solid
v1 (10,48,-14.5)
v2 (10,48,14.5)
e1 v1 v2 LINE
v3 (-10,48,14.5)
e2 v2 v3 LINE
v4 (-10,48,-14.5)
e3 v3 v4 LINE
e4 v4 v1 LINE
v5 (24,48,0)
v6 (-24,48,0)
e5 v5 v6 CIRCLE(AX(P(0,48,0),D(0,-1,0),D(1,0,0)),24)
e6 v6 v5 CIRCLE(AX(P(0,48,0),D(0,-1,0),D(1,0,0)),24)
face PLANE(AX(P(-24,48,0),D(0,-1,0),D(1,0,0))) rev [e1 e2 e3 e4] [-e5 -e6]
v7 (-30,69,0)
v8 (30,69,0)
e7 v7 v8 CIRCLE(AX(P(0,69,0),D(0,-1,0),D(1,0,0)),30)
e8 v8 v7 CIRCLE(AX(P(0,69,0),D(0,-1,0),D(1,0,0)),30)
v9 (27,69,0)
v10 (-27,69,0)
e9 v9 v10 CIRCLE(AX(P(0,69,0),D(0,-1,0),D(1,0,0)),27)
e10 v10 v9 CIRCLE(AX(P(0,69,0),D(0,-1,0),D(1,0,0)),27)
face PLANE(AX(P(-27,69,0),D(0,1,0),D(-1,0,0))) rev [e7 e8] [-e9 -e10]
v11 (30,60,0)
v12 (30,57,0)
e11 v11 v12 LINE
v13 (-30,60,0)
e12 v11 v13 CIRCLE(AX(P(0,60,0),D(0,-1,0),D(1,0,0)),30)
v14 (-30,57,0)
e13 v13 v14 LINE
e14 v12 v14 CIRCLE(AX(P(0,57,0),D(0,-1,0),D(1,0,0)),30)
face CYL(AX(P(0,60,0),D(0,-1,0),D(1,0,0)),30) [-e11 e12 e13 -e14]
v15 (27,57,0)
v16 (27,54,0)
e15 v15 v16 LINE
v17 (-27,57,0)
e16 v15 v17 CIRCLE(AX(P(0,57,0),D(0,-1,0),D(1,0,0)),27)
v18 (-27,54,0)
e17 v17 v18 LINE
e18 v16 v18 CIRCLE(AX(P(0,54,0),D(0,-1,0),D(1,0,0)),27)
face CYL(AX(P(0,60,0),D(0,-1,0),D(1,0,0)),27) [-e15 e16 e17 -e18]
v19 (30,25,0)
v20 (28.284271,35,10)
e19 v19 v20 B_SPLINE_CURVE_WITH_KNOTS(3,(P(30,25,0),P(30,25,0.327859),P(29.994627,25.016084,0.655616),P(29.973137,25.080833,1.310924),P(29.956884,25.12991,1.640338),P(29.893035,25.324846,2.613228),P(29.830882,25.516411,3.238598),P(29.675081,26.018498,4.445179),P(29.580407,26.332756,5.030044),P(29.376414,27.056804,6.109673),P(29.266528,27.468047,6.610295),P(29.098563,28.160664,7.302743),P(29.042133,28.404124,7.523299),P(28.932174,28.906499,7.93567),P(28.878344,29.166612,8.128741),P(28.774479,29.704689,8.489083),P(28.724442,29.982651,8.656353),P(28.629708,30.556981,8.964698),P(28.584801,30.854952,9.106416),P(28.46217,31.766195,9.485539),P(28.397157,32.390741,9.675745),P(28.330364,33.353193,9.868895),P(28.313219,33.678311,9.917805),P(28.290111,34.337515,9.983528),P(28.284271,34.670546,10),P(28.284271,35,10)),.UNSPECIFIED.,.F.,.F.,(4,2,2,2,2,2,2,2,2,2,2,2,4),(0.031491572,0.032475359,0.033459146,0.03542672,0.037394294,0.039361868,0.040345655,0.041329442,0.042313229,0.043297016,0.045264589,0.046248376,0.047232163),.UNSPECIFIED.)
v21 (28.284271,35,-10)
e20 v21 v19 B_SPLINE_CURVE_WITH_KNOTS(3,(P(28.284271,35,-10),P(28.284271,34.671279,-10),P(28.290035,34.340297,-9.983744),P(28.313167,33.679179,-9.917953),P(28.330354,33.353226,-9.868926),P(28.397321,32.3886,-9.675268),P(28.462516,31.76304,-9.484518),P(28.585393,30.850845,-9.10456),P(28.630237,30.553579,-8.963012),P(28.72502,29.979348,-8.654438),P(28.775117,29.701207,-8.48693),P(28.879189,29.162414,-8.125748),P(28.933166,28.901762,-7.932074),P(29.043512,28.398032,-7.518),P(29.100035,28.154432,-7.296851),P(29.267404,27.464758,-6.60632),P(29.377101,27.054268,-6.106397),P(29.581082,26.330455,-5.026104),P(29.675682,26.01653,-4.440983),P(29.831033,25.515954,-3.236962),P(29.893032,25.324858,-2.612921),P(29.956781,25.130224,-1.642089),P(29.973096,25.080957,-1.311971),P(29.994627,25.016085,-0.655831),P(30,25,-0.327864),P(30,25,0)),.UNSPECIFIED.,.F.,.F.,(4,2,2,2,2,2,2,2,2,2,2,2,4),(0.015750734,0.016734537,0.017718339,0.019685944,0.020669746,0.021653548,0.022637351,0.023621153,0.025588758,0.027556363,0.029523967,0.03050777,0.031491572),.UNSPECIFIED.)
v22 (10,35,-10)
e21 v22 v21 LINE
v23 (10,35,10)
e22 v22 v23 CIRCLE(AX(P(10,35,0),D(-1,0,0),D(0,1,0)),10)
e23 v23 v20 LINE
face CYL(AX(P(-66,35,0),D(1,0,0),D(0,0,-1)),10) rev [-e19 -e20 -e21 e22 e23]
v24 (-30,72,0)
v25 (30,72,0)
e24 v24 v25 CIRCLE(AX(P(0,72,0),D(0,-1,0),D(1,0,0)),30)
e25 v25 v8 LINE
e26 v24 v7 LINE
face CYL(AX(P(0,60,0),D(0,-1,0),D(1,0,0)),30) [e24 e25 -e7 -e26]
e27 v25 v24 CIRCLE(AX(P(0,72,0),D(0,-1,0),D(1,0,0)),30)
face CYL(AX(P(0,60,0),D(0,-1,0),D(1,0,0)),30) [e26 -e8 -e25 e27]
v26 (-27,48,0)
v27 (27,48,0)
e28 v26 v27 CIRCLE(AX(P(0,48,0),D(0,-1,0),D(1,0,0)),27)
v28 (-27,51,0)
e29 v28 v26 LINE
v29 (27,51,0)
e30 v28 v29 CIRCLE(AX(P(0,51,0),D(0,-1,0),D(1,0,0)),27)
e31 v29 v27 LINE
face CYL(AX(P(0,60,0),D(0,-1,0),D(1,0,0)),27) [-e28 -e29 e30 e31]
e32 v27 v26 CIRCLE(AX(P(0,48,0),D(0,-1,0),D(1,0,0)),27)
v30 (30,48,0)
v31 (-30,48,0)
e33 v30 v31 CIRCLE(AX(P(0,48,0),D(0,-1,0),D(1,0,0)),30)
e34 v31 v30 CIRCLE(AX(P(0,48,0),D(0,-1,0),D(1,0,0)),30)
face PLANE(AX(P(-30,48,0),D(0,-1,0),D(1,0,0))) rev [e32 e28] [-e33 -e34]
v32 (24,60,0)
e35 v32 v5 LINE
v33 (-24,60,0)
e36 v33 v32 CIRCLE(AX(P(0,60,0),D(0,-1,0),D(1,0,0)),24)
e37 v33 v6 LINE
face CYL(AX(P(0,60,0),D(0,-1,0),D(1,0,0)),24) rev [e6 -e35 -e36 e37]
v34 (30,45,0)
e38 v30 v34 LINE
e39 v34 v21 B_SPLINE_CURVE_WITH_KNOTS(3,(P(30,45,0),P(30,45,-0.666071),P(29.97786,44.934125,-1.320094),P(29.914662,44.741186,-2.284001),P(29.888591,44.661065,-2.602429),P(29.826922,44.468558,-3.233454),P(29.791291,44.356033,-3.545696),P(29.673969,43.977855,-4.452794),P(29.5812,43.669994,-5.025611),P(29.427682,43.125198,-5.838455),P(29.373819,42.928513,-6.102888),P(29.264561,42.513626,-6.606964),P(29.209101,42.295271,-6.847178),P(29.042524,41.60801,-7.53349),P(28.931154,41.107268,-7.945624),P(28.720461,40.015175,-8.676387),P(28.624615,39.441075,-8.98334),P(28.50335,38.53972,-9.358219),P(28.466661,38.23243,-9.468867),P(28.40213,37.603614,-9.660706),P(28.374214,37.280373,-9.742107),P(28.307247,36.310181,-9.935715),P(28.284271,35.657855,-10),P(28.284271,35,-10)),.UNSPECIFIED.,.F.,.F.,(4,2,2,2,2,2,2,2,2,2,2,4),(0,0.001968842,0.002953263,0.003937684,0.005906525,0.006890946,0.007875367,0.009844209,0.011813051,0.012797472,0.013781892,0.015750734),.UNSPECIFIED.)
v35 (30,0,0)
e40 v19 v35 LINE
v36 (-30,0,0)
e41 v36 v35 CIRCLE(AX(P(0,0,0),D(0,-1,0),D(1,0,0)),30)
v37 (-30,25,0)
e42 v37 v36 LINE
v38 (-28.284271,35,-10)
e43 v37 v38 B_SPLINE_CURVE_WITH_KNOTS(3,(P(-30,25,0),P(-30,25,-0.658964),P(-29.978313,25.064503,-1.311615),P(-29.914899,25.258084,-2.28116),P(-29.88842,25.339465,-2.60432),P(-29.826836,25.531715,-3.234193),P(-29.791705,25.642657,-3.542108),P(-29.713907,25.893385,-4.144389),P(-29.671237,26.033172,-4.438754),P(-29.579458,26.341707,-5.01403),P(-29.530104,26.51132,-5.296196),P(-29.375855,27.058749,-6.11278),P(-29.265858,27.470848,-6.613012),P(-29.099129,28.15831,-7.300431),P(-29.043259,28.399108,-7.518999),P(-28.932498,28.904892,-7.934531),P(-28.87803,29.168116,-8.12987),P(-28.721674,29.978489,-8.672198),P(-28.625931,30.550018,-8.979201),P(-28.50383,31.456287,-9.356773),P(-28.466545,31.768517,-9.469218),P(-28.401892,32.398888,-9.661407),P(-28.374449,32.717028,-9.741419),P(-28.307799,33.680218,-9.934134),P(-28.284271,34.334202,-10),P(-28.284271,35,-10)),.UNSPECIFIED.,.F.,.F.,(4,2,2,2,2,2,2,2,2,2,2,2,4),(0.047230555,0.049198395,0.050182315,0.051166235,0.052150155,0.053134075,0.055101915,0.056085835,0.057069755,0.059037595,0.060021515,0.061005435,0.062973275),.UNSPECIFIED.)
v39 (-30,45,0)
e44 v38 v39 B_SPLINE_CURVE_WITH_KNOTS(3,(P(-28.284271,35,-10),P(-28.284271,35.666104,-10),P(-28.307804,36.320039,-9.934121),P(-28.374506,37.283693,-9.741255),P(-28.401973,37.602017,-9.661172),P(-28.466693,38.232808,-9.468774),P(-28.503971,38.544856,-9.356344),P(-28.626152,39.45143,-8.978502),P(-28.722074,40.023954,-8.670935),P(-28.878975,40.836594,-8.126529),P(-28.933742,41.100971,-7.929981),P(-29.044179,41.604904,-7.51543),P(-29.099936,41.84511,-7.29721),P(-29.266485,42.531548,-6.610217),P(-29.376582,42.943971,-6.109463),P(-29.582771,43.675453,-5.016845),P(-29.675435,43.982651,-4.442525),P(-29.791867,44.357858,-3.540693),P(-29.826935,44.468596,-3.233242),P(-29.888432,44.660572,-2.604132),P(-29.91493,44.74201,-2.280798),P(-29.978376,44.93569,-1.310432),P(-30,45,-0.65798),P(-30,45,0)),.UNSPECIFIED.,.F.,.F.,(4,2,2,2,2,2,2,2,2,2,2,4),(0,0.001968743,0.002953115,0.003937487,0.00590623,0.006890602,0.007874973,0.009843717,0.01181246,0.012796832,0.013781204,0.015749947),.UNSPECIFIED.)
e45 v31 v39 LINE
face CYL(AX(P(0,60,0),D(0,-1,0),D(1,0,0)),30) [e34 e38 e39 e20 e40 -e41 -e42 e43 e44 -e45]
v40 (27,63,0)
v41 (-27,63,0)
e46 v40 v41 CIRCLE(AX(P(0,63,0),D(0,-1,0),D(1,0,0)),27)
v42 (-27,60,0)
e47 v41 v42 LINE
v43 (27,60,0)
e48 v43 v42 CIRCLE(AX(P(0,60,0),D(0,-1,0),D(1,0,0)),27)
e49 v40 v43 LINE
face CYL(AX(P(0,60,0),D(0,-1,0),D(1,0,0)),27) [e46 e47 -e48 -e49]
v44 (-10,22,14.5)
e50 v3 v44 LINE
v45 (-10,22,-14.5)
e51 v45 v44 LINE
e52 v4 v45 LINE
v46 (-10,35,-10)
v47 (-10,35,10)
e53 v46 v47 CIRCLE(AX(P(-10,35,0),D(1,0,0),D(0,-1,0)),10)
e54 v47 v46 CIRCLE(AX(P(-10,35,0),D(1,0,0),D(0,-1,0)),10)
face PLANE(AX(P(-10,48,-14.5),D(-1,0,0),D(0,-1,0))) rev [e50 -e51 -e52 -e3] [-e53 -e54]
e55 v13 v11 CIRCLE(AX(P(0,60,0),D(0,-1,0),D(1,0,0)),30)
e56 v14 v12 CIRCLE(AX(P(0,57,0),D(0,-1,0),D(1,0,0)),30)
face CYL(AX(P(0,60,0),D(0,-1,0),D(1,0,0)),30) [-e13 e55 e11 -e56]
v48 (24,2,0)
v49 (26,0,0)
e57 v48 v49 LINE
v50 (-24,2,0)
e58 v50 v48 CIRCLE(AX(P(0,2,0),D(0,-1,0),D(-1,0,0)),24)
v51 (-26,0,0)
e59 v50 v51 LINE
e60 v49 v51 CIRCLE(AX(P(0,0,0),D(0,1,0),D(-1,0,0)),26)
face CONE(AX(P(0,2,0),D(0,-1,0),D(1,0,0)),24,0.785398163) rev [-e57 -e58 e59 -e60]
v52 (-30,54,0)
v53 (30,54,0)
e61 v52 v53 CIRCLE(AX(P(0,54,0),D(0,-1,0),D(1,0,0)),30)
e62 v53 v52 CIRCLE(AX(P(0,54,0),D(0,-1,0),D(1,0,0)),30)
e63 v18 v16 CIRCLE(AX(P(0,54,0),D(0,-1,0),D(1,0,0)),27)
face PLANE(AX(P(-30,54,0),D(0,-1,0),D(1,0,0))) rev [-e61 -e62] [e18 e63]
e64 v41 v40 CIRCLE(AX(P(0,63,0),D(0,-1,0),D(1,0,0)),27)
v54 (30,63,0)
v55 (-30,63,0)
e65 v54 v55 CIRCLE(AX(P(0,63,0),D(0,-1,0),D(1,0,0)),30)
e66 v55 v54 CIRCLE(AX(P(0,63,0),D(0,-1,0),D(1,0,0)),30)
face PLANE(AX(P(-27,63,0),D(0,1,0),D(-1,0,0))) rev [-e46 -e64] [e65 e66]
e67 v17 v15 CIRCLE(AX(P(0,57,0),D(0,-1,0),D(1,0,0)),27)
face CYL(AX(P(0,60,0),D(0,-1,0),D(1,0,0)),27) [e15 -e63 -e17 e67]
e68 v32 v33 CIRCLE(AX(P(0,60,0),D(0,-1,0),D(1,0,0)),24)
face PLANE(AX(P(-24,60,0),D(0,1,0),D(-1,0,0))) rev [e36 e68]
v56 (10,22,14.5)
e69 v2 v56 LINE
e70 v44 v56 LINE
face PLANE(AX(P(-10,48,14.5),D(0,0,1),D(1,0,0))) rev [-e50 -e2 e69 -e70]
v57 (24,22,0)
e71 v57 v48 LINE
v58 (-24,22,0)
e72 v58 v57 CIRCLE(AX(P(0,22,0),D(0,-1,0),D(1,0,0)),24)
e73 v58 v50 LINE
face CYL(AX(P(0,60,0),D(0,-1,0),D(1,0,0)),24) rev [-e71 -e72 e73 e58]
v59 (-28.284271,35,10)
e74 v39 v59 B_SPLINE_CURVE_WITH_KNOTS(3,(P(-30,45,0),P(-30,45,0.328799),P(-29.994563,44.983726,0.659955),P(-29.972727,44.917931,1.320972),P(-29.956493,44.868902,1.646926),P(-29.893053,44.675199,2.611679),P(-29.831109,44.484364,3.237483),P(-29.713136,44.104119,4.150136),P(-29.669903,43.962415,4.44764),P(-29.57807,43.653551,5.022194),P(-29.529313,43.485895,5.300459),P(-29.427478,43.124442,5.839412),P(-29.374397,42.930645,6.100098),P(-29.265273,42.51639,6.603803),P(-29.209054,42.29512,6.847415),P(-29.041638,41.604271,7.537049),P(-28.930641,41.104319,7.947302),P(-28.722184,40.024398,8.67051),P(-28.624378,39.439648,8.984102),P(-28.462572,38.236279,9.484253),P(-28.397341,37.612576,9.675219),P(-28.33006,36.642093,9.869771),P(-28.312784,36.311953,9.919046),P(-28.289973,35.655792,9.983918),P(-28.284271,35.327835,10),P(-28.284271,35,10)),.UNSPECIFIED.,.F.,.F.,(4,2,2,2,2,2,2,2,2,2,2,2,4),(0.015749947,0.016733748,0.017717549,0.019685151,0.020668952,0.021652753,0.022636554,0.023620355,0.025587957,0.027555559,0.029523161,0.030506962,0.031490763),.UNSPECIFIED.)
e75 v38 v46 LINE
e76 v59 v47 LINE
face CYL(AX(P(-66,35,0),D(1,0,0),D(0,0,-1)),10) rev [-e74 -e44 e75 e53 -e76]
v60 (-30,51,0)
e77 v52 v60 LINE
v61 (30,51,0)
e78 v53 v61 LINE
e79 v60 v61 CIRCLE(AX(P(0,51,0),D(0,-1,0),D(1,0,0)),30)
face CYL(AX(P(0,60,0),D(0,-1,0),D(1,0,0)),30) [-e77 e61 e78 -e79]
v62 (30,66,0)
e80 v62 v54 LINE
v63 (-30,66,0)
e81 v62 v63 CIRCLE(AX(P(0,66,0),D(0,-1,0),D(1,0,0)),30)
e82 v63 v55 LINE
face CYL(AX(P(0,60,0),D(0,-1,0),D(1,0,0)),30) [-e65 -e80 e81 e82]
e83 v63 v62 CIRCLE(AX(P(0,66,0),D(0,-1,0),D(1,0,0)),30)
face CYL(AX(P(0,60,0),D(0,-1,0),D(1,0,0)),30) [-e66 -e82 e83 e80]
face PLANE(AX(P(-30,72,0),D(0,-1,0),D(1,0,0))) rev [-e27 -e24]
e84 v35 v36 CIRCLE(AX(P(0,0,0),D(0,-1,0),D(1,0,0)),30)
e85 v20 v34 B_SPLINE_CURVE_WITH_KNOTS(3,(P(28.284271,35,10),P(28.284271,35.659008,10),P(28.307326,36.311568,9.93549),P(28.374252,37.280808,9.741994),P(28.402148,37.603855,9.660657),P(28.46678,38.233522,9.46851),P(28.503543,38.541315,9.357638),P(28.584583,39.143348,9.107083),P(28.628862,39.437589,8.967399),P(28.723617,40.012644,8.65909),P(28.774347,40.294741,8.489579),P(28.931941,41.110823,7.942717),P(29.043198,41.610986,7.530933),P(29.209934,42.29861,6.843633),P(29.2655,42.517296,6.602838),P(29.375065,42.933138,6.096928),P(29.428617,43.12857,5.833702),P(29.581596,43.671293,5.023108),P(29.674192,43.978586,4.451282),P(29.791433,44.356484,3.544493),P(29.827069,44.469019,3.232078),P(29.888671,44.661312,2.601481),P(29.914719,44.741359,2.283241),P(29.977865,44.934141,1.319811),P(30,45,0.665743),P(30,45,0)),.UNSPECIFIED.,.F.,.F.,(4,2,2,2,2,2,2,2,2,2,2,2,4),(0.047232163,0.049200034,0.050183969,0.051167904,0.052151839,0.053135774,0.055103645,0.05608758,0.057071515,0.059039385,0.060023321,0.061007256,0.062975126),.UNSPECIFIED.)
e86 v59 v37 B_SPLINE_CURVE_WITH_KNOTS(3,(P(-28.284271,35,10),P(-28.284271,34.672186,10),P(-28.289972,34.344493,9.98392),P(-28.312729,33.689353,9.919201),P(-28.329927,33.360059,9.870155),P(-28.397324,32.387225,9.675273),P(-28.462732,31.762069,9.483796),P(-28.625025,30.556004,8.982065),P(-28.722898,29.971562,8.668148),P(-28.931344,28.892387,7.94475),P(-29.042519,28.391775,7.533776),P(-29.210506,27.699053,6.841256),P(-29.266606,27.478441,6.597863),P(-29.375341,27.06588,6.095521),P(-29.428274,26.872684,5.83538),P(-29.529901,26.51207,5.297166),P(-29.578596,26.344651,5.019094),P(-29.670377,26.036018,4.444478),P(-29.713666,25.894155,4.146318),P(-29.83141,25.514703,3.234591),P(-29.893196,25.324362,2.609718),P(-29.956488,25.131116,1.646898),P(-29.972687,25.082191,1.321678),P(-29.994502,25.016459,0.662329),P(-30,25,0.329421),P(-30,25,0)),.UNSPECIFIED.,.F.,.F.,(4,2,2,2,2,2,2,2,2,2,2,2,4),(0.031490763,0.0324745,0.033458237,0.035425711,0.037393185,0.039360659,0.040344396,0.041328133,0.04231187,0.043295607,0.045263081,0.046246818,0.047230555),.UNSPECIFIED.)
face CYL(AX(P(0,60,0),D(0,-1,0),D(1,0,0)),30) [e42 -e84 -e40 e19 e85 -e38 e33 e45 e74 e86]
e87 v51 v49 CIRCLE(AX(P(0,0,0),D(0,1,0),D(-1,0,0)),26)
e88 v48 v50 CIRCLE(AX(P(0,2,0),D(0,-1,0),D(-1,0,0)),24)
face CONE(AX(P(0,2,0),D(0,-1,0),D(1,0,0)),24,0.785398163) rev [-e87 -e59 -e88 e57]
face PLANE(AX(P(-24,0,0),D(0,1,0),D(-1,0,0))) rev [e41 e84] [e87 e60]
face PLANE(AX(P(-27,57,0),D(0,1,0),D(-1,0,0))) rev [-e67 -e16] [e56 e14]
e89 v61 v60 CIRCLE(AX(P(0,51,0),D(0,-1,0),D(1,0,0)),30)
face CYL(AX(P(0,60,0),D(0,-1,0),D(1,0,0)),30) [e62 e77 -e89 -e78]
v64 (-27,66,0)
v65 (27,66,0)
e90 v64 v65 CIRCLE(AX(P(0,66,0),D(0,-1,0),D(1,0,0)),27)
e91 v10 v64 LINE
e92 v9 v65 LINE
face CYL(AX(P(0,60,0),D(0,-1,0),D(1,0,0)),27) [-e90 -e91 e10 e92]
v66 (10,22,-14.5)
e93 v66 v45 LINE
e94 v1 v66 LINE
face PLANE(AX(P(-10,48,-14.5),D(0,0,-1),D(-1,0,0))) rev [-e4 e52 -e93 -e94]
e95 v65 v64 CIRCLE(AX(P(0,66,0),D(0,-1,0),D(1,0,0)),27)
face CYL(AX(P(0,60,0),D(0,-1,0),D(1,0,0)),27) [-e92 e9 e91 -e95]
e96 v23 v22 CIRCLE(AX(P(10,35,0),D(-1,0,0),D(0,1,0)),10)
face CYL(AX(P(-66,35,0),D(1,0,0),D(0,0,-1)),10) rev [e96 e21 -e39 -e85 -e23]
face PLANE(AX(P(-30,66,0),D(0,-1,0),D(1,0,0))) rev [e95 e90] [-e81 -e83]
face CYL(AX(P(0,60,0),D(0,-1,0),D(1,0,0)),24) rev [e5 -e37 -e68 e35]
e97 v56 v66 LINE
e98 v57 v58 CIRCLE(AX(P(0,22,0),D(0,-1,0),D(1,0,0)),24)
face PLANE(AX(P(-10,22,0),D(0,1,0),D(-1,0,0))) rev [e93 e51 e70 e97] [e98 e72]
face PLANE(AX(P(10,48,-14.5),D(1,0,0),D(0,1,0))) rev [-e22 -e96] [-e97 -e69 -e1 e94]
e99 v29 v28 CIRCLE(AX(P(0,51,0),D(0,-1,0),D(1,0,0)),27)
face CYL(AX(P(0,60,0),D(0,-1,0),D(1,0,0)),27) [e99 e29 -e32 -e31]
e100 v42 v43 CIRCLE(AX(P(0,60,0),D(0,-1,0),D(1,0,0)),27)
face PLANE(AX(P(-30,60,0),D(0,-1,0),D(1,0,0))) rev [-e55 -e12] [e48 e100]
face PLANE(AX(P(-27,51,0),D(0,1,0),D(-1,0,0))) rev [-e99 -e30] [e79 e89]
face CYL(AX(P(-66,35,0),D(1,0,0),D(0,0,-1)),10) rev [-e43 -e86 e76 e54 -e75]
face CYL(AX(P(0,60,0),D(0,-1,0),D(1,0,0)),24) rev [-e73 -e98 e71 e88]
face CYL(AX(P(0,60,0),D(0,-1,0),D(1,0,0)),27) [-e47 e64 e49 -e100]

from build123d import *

# Parameters (mm, degrees)
PIN_BORE_SKETCH_R         = 10
GUDGEON_PIN_BORE_20_DEPTH = 66
EDGE_CHAMFER_2X45_SIZE    = 2
INNER_CAVITY_SKETCH_W     = 20
INNER_CAVITY_SKETCH_H     = 29
INNER_CAVITY_CUT_DEPTH    = 48


with BuildPart() as part:
    # Piston Profile Sketch → Piston Body Revolve (revolve)
    with BuildSketch(Plane.XY, mode=Mode.PRIVATE) as piston_body_revolve_sk:
        Polygon((-24, 0), (-30, 0), (-30, 48), (-27, 48), (-27, 51), (-30, 51), (-30, 54), (-27, 54), (-27, 57), (-30, 57), (-30, 60), (-27, 60), (-27, 63), (-30, 63), (-30, 66), (-27, 66), (-27, 69), (-30, 69), (-30, 72), (0, 72), (0, 60), (-24, 60), (-24, 48), (-10, 48), (-10, 22), (-24, 22), align=None)
    revolve(piston_body_revolve_sk.sketch.rotate(Axis((0, 60, 0), (0, 1, 0)), 180), axis=Axis((0, 60, 0), (0, 1, 0)))

    # Pin Bore Sketch → Gudgeon Pin Bore Ø20 (cut, symmetric)
    with BuildSketch(Plane(origin=(0, 0, 0), x_dir=(0, 0, -1), z_dir=(1, 0, 0))):
        with Locations(Location((0, 35, 0), (0, 0, 270))):
            Circle(PIN_BORE_SKETCH_R)
    extrude(amount=GUDGEON_PIN_BORE_20_DEPTH, both=True, mode=Mode.SUBTRACT)

    # Edge Chamfer 2x45°
    edge_chamfer_2x45_edges = [part.edges().sort_by_distance(p)[0] for p in [
        (-24, 0, 0),
    ]]
    chamfer(edge_chamfer_2x45_edges, length=EDGE_CHAMFER_2X45_SIZE)

    # Inner Cavity Sketch → Inner Cavity Cut (cut)
    with BuildSketch(Plane.XZ):
        Rectangle(INNER_CAVITY_SKETCH_W, INNER_CAVITY_SKETCH_H)
    extrude(amount=-INNER_CAVITY_CUT_DEPTH, mode=Mode.SUBTRACT)


solid = part.part
